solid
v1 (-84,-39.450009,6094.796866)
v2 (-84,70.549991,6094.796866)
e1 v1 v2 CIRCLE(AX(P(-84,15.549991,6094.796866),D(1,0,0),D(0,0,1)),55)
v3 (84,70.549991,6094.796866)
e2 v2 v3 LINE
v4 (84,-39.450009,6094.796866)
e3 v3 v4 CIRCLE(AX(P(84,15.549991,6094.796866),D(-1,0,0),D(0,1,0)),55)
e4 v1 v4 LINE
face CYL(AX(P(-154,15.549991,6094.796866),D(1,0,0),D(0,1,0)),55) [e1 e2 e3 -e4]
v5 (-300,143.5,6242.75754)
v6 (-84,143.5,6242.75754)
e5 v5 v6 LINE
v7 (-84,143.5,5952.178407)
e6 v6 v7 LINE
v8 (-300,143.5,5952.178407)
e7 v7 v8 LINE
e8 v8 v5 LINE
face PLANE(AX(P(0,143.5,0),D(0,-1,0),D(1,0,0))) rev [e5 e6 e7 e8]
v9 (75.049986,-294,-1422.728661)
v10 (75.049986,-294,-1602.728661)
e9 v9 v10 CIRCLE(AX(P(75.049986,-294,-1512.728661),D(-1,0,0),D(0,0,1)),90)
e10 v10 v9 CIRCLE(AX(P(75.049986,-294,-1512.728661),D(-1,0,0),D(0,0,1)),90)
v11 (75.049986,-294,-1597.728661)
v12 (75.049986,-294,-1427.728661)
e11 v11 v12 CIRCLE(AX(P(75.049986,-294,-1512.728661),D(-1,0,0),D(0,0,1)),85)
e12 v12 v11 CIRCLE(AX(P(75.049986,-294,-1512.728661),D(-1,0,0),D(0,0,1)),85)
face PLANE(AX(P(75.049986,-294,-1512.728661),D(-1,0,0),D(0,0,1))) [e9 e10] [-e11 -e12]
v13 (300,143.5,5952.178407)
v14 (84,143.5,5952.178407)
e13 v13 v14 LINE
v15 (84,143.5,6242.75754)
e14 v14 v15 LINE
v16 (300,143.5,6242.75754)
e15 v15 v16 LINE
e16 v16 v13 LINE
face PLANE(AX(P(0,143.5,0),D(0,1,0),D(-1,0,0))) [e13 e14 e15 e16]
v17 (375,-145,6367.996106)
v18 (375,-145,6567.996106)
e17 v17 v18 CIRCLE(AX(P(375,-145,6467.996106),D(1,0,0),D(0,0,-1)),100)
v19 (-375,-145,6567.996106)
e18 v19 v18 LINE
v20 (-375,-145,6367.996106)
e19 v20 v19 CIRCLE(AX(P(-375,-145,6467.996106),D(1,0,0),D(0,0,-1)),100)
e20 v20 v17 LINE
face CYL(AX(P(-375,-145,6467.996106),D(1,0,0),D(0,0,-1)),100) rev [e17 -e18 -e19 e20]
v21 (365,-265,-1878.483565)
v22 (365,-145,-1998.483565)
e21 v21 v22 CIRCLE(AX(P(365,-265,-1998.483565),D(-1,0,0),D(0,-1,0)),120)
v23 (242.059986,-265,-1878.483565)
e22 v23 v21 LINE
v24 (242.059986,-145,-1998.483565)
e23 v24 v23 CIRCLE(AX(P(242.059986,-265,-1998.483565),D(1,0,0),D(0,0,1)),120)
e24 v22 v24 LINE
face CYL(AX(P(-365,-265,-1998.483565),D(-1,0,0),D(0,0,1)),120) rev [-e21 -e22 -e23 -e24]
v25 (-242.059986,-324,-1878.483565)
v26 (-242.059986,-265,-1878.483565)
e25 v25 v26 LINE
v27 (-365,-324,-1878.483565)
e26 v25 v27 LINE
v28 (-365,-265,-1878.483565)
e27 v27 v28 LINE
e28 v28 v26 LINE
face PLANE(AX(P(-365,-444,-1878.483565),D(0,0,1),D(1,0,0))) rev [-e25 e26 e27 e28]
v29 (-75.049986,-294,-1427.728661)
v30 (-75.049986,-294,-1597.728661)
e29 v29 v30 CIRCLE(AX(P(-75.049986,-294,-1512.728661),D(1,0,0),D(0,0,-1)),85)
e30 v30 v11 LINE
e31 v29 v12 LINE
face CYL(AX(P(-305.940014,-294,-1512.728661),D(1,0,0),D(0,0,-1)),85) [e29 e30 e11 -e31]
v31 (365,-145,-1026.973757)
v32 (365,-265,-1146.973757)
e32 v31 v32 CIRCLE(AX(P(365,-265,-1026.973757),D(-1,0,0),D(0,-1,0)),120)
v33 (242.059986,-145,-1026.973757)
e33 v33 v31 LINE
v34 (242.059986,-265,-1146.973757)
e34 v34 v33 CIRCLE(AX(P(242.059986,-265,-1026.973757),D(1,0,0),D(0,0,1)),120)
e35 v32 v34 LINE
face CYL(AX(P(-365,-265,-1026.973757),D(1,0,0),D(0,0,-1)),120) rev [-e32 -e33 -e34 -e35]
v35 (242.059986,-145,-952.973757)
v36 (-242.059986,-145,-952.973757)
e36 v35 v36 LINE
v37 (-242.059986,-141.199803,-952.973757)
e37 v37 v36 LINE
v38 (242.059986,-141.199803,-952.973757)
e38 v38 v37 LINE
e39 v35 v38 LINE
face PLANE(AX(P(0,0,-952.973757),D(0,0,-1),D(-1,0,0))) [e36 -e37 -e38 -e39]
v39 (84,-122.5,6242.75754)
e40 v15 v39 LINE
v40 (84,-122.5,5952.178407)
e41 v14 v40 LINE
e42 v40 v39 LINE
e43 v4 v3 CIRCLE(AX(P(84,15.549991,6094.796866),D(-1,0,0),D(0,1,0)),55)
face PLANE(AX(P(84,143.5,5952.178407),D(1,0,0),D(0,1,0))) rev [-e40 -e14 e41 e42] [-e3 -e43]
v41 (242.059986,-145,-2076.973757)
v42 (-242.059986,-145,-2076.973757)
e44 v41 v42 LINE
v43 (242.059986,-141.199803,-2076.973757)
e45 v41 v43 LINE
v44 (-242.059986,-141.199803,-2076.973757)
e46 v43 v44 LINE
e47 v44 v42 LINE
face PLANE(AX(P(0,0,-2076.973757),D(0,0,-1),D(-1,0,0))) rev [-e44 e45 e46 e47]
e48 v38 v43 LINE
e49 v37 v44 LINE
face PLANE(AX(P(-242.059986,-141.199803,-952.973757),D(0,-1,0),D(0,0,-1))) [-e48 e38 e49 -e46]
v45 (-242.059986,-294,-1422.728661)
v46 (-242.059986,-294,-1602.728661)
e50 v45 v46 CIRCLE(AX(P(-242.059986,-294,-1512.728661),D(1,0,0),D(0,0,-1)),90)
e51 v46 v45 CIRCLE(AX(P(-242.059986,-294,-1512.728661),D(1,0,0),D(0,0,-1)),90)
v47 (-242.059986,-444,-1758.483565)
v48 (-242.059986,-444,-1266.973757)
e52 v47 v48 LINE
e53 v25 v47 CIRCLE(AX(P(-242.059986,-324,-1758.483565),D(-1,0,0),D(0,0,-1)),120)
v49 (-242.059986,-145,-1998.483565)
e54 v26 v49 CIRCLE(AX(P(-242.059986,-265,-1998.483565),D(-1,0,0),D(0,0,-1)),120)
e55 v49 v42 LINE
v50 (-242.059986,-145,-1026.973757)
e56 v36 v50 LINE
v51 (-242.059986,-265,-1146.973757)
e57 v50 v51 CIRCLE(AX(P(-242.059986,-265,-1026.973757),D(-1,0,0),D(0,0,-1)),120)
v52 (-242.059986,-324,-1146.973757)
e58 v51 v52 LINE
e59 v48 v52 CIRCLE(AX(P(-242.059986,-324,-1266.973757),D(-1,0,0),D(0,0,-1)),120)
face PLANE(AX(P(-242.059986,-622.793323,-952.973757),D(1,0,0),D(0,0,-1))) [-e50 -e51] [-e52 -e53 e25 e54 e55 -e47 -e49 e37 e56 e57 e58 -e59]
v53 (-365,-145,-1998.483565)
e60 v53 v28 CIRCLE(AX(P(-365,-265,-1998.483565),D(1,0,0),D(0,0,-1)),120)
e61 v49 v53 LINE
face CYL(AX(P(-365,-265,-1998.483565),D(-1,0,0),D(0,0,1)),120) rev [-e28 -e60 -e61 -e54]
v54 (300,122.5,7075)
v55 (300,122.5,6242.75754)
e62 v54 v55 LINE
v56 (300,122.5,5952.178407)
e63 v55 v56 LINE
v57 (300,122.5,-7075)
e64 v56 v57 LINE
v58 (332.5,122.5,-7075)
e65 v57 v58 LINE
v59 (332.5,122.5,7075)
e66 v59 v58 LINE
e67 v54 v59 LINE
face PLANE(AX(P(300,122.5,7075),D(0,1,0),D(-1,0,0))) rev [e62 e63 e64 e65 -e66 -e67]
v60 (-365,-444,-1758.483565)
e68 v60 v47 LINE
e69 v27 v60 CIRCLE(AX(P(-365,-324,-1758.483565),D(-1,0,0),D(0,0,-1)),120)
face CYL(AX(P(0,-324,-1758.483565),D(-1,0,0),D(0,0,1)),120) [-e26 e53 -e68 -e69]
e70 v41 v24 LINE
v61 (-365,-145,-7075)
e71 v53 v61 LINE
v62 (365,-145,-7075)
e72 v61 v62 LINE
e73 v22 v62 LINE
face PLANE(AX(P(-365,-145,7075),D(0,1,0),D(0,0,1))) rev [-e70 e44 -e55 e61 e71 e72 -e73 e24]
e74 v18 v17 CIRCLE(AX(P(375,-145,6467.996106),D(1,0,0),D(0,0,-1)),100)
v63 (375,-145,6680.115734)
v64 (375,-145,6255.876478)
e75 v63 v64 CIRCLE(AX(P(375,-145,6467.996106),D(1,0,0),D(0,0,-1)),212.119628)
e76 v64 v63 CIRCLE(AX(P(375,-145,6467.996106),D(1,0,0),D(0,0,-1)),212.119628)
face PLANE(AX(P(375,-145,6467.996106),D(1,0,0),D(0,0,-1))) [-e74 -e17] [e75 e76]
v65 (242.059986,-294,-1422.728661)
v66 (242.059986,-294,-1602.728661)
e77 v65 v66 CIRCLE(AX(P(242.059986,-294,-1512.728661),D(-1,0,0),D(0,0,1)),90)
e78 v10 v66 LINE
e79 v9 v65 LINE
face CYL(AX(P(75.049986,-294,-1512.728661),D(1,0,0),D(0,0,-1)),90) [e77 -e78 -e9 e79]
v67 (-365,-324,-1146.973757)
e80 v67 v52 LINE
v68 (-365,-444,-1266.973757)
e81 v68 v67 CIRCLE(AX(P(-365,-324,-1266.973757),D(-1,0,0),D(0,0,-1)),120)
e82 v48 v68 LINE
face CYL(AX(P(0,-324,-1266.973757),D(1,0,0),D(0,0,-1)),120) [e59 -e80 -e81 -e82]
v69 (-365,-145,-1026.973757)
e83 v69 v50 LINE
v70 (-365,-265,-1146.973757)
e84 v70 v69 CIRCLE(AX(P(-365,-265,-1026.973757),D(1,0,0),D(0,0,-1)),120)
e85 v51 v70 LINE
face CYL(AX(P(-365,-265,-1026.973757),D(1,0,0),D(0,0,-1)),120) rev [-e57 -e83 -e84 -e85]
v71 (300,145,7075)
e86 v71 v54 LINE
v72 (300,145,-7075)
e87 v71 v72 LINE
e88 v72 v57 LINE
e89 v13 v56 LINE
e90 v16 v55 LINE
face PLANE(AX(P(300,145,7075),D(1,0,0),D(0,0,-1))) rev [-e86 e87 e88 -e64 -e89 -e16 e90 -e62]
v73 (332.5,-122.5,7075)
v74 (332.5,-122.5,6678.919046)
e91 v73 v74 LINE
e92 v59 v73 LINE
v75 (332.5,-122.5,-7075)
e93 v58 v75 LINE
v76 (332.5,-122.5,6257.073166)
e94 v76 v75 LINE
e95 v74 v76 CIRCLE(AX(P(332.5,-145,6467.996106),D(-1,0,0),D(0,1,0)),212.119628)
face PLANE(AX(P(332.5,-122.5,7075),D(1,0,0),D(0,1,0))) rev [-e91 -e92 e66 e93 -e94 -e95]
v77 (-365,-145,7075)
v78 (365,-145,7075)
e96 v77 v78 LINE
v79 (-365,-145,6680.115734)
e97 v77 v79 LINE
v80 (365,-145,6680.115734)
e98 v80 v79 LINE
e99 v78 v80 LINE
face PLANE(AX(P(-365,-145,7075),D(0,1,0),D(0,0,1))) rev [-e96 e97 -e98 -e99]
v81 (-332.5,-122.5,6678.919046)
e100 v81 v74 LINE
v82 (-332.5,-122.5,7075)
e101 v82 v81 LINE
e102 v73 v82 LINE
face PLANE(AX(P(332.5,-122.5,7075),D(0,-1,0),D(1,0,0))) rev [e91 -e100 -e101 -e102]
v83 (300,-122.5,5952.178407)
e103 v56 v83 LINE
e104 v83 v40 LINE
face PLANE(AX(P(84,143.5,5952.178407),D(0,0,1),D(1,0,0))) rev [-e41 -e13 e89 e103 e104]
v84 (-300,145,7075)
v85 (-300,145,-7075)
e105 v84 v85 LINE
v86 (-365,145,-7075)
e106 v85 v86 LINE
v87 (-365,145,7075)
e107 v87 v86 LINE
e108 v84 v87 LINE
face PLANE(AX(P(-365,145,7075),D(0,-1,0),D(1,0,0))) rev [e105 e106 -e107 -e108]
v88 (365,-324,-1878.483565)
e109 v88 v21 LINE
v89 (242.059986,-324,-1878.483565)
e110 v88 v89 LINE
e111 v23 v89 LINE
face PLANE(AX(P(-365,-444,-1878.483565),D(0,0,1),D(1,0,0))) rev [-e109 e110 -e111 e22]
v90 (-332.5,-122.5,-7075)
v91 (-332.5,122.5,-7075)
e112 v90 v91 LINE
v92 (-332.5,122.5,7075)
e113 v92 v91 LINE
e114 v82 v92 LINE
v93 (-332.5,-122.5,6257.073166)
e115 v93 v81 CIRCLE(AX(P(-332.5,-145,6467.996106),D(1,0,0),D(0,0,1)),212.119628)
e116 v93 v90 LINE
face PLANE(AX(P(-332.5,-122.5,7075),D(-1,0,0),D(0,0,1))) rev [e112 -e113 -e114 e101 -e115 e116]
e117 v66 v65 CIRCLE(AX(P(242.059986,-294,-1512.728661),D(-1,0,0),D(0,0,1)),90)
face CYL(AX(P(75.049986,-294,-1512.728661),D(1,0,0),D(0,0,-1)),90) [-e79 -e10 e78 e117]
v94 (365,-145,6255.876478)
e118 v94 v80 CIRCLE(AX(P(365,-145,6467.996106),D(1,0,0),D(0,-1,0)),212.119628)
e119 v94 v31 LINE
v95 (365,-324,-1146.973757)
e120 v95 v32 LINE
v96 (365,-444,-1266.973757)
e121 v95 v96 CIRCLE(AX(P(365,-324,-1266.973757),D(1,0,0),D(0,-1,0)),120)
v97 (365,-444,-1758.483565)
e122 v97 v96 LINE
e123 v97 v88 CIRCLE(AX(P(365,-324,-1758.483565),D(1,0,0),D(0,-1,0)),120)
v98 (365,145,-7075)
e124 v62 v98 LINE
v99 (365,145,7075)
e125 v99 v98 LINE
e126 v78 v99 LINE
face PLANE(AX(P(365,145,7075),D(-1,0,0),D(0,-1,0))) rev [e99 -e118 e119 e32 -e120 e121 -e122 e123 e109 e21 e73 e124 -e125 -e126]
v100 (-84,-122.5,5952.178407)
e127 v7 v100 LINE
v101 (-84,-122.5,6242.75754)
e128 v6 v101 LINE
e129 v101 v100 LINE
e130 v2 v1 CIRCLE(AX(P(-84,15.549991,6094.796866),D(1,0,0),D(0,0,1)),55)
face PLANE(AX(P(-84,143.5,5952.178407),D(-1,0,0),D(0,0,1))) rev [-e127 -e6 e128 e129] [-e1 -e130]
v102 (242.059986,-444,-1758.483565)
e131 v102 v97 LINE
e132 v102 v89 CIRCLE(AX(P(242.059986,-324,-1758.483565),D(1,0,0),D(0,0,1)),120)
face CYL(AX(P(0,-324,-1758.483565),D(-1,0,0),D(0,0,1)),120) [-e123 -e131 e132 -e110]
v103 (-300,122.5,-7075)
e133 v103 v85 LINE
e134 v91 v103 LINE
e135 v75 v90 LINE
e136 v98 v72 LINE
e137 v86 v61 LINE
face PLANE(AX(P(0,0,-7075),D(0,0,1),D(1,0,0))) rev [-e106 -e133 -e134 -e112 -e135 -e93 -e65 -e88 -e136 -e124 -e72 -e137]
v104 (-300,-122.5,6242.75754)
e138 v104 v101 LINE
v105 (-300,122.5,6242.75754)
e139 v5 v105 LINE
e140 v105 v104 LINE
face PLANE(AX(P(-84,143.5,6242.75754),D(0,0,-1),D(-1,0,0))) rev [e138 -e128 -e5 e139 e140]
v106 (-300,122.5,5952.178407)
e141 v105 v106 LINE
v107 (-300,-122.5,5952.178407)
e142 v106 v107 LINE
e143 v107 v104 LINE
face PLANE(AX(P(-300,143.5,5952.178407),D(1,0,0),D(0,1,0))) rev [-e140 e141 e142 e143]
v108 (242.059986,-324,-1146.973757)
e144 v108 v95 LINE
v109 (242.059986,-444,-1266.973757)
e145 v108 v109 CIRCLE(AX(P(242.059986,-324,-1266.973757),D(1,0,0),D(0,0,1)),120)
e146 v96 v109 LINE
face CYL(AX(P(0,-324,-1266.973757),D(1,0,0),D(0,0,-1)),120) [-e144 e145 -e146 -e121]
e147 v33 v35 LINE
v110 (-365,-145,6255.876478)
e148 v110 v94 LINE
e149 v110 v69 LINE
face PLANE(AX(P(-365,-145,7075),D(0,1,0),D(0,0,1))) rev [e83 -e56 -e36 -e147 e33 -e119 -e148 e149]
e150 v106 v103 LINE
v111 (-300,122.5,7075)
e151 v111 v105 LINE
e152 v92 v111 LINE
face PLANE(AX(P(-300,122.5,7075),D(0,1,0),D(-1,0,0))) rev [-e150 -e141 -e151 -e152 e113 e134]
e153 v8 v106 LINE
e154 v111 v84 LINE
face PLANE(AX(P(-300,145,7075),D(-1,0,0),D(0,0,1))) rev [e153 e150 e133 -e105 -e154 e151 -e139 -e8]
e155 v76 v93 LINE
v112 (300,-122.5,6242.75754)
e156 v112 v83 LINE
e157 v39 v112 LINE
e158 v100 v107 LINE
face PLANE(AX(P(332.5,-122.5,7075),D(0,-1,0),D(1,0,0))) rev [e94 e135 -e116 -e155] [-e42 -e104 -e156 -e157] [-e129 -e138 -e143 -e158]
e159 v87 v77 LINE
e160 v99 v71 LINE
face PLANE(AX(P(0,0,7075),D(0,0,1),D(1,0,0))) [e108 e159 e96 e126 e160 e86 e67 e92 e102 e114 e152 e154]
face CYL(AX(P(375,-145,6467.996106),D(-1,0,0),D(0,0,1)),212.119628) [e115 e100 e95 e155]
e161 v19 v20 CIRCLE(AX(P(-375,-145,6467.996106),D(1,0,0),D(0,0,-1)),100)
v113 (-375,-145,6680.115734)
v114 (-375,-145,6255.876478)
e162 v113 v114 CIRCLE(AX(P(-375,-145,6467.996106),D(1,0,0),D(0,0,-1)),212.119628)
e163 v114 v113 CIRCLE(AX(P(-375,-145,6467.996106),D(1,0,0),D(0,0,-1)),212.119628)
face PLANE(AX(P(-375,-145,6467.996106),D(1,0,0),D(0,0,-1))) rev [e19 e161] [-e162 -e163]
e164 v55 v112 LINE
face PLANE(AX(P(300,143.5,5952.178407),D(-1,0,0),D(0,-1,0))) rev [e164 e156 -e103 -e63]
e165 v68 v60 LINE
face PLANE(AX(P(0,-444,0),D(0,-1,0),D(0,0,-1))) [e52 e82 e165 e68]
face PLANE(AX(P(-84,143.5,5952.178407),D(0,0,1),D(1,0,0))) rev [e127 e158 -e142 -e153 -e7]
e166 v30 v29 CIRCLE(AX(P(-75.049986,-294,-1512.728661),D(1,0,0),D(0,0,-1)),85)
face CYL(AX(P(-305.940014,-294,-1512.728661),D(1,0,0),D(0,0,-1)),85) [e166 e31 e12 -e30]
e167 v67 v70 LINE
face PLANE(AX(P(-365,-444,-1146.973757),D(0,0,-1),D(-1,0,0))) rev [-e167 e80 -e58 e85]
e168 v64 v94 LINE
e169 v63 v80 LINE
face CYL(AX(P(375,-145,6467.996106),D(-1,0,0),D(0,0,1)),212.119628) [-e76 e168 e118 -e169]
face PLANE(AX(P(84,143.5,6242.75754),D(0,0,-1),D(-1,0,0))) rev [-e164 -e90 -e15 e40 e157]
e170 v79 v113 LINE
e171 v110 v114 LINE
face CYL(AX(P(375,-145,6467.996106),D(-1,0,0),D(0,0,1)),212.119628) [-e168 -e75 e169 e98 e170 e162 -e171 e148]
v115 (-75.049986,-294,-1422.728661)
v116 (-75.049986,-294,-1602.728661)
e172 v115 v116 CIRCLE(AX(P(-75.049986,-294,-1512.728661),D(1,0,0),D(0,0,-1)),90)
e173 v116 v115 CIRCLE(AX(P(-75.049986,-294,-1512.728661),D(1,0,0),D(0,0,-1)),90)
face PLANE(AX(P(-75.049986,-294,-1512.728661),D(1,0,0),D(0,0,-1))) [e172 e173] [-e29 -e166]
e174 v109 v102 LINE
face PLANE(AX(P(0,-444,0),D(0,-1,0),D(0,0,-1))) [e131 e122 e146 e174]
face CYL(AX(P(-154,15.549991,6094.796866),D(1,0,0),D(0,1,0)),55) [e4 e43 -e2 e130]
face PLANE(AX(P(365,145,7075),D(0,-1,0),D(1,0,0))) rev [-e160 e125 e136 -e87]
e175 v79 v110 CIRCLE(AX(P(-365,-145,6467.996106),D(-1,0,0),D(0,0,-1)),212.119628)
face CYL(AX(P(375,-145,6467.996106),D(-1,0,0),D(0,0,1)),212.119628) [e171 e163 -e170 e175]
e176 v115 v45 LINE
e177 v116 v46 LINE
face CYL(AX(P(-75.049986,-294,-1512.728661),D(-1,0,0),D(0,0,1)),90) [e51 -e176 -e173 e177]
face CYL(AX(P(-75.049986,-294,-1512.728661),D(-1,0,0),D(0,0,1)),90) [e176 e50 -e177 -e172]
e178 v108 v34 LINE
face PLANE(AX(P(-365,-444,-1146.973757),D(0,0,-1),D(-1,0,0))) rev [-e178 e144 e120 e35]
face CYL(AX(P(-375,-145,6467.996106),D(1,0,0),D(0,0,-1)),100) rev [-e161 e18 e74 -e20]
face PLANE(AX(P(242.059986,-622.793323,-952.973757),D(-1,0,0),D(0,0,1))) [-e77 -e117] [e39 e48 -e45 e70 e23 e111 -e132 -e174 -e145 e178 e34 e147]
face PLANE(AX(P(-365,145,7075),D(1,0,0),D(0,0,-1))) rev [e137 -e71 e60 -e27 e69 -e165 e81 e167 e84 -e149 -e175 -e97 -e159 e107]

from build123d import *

# Parameters (mm, degrees)
BOSS_EXTRUDE1_DEPTH     = 7075
SKETCH4_W               = 730
SKETCH4_H               = 731.509808534
BOSS_EXTRUDE2_DEPTH     = 299
FILLET1_R               = 120
FILLET2_R               = 120
SKETCH7_R               = 212.119628044
BOSS_EXTRUDE3_DEPTH     = 375
SKETCH8_R               = 87.5
BOSS_EXTRUDE4_DEPTH     = 425
CUT_EXTRUDE1_DEPTH      = 194
CUT_EXTRUDE1_DEPTH_BACK = 930
SKETCH9_W               = 484.11997185
SKETCH9_H               = 481.593519394
SKETCH12_R              = 85
BOSS_EXTRUDE5_DEPTH     = 548
SKETCH14_R              = 90
BOSS_EXTRUDE6_DEPTH     = 167.01
BOSS_EXTRUDE7_START     = 167.01
SKETCH15_R              = 90
BOSS_EXTRUDE7_DEPTH     = 167.01
SKETCH16_W              = 216
SKETCH16_H              = 290.579133159
BOSS_EXTRUDE8_DEPTH     = 266
SKETCH17_R              = 55
BOSS_EXTRUDE9_DEPTH     = 238
SKETCH18_R              = 87.5
CUT_EXTRUDE2_DEPTH      = 7140.696141994
SKETCH19_R              = 100
CUT_EXTRUDE3_DEPTH      = 7129.482377056


with BuildPart() as part:
    # Sketch1 → Boss-Extrude1 (new, symmetric)
    with BuildSketch(Plane.XY):
        Polygon((-300, 145), (-300, 122.5), (-332.5, 122.5), (-332.5, -122.5), (332.5, -122.5), (332.5, 122.5), (300, 122.5), (300, 145), (365, 145), (365, -145), (-365, -145), (-365, 145), align=None)
    extrude(amount=BOSS_EXTRUDE1_DEPTH, both=True)

    # Sketch4 → Boss-Extrude2 (add)
    with BuildSketch(Plane.XZ.offset(145)):
        with Locations((0, -1512.728660923)):
            Rectangle(SKETCH4_W, SKETCH4_H)
    extrude(amount=BOSS_EXTRUDE2_DEPTH)

    # Fillet1
    fillet1_edges = [part.edges().sort_by_distance(p)[0] for p in [
        (0, -444, -1146.973756656),
        (0, -444, -1878.48356519),
    ]]
    fillet(fillet1_edges, radius=FILLET1_R)

    # Fillet2
    fillet2_edges = [part.edges().sort_by_distance(p)[0] for p in [
        (0, -145, -1146.973756656),
        (0, -145, -1878.48356519),
    ]]
    fillet(fillet2_edges, radius=FILLET2_R)

    # Sketch7 → Boss-Extrude3 (add, symmetric)
    with BuildSketch(Plane(origin=(0, 0, 0), x_dir=(0, 0, -1), z_dir=(1, 0, 0))):
        with Locations((-6467.996106232, -145)):
            Circle(SKETCH7_R)
    extrude(amount=BOSS_EXTRUDE3_DEPTH, both=True)

    # Sketch8 → Boss-Extrude4 (add, symmetric)
    with BuildSketch(Plane(origin=(0, 0, 0), x_dir=(0, 0, -1), z_dir=(1, 0, 0))):
        with Locations((-6467.996106232, -145)):
            Circle(SKETCH8_R)
    extrude(amount=BOSS_EXTRUDE4_DEPTH, both=True)

    # Sketch9 → Cut-Extrude1 (cut, two sides: drawn at the far end of the back side and taken through both)
    with BuildSketch(Plane.XY.offset(-1146.973756656).offset(-CUT_EXTRUDE1_DEPTH_BACK)):
        with Locations((0, -381.996563184)):
            Rectangle(SKETCH9_W, SKETCH9_H)
    extrude(amount=CUT_EXTRUDE1_DEPTH + CUT_EXTRUDE1_DEPTH_BACK, mode=Mode.SUBTRACT)

    # Sketch12 → Boss-Extrude5 (add)
    with BuildSketch(Plane.ZY.offset(-242.059985925)):
        with Locations(Location((-1512.728660923, -294, 0), (0, 0, 180))):
            Circle(SKETCH12_R)
    extrude(amount=BOSS_EXTRUDE5_DEPTH)

    # Sketch14 → Boss-Extrude6 (add)
    with BuildSketch(Plane.ZY.offset(-242.059985925)):
        with Locations((-1512.728660923, -294)):
            Circle(SKETCH14_R)
    extrude(amount=BOSS_EXTRUDE6_DEPTH)

    # Sketch15 → Boss-Extrude7 (add)
    with BuildSketch(Plane(origin=(-242.059985925, 0, 0), x_dir=(0, 0, -1), z_dir=(1, 0, 0)).offset(BOSS_EXTRUDE7_START)):
        with Locations(Location((1512.728660923, -294, 0), (0, 0, 180))):
            Circle(SKETCH15_R)
    extrude(amount=-BOSS_EXTRUDE7_DEPTH)

    # Sketch16 → Boss-Extrude8 (add)
    with BuildSketch(Plane(origin=(0, -122.5, 0), x_dir=(1, 0, 0), z_dir=(0, 1, 0))):
        with Locations((192, -6097.467973851)):
            Rectangle(SKETCH16_W, SKETCH16_H)
        with Locations((-192, -6097.467973851)):
            Rectangle(SKETCH16_W, SKETCH16_H)
    extrude(amount=BOSS_EXTRUDE8_DEPTH)

    # Sketch17 → Boss-Extrude9 (add)
    with BuildSketch(Plane.ZY.offset(-84)):
        with Locations(Location((6094.796866122, 15.549991037, 0), (0, 0, 90))):
            Circle(SKETCH17_R)
    extrude(amount=BOSS_EXTRUDE9_DEPTH)

    # Sketch18 → Cut-Extrude2 (cut, through all)
    with BuildSketch(Plane(origin=(425, 0, 0), x_dir=(0, 0, -1), z_dir=(1, 0, 0))):
        with Locations((-6467.996106232, -145)):
            Circle(SKETCH18_R)
    extrude(amount=-CUT_EXTRUDE2_DEPTH, mode=Mode.SUBTRACT)

    # Sketch19 → Cut-Extrude3 (cut, through all)
    with BuildSketch(Plane(origin=(375, 0, 0), x_dir=(0, 0, -1), z_dir=(1, 0, 0))):
        with Locations((-6467.996106232, -145)):
            Circle(SKETCH19_R)
    extrude(amount=-CUT_EXTRUDE3_DEPTH, mode=Mode.SUBTRACT)


solid = part.part
